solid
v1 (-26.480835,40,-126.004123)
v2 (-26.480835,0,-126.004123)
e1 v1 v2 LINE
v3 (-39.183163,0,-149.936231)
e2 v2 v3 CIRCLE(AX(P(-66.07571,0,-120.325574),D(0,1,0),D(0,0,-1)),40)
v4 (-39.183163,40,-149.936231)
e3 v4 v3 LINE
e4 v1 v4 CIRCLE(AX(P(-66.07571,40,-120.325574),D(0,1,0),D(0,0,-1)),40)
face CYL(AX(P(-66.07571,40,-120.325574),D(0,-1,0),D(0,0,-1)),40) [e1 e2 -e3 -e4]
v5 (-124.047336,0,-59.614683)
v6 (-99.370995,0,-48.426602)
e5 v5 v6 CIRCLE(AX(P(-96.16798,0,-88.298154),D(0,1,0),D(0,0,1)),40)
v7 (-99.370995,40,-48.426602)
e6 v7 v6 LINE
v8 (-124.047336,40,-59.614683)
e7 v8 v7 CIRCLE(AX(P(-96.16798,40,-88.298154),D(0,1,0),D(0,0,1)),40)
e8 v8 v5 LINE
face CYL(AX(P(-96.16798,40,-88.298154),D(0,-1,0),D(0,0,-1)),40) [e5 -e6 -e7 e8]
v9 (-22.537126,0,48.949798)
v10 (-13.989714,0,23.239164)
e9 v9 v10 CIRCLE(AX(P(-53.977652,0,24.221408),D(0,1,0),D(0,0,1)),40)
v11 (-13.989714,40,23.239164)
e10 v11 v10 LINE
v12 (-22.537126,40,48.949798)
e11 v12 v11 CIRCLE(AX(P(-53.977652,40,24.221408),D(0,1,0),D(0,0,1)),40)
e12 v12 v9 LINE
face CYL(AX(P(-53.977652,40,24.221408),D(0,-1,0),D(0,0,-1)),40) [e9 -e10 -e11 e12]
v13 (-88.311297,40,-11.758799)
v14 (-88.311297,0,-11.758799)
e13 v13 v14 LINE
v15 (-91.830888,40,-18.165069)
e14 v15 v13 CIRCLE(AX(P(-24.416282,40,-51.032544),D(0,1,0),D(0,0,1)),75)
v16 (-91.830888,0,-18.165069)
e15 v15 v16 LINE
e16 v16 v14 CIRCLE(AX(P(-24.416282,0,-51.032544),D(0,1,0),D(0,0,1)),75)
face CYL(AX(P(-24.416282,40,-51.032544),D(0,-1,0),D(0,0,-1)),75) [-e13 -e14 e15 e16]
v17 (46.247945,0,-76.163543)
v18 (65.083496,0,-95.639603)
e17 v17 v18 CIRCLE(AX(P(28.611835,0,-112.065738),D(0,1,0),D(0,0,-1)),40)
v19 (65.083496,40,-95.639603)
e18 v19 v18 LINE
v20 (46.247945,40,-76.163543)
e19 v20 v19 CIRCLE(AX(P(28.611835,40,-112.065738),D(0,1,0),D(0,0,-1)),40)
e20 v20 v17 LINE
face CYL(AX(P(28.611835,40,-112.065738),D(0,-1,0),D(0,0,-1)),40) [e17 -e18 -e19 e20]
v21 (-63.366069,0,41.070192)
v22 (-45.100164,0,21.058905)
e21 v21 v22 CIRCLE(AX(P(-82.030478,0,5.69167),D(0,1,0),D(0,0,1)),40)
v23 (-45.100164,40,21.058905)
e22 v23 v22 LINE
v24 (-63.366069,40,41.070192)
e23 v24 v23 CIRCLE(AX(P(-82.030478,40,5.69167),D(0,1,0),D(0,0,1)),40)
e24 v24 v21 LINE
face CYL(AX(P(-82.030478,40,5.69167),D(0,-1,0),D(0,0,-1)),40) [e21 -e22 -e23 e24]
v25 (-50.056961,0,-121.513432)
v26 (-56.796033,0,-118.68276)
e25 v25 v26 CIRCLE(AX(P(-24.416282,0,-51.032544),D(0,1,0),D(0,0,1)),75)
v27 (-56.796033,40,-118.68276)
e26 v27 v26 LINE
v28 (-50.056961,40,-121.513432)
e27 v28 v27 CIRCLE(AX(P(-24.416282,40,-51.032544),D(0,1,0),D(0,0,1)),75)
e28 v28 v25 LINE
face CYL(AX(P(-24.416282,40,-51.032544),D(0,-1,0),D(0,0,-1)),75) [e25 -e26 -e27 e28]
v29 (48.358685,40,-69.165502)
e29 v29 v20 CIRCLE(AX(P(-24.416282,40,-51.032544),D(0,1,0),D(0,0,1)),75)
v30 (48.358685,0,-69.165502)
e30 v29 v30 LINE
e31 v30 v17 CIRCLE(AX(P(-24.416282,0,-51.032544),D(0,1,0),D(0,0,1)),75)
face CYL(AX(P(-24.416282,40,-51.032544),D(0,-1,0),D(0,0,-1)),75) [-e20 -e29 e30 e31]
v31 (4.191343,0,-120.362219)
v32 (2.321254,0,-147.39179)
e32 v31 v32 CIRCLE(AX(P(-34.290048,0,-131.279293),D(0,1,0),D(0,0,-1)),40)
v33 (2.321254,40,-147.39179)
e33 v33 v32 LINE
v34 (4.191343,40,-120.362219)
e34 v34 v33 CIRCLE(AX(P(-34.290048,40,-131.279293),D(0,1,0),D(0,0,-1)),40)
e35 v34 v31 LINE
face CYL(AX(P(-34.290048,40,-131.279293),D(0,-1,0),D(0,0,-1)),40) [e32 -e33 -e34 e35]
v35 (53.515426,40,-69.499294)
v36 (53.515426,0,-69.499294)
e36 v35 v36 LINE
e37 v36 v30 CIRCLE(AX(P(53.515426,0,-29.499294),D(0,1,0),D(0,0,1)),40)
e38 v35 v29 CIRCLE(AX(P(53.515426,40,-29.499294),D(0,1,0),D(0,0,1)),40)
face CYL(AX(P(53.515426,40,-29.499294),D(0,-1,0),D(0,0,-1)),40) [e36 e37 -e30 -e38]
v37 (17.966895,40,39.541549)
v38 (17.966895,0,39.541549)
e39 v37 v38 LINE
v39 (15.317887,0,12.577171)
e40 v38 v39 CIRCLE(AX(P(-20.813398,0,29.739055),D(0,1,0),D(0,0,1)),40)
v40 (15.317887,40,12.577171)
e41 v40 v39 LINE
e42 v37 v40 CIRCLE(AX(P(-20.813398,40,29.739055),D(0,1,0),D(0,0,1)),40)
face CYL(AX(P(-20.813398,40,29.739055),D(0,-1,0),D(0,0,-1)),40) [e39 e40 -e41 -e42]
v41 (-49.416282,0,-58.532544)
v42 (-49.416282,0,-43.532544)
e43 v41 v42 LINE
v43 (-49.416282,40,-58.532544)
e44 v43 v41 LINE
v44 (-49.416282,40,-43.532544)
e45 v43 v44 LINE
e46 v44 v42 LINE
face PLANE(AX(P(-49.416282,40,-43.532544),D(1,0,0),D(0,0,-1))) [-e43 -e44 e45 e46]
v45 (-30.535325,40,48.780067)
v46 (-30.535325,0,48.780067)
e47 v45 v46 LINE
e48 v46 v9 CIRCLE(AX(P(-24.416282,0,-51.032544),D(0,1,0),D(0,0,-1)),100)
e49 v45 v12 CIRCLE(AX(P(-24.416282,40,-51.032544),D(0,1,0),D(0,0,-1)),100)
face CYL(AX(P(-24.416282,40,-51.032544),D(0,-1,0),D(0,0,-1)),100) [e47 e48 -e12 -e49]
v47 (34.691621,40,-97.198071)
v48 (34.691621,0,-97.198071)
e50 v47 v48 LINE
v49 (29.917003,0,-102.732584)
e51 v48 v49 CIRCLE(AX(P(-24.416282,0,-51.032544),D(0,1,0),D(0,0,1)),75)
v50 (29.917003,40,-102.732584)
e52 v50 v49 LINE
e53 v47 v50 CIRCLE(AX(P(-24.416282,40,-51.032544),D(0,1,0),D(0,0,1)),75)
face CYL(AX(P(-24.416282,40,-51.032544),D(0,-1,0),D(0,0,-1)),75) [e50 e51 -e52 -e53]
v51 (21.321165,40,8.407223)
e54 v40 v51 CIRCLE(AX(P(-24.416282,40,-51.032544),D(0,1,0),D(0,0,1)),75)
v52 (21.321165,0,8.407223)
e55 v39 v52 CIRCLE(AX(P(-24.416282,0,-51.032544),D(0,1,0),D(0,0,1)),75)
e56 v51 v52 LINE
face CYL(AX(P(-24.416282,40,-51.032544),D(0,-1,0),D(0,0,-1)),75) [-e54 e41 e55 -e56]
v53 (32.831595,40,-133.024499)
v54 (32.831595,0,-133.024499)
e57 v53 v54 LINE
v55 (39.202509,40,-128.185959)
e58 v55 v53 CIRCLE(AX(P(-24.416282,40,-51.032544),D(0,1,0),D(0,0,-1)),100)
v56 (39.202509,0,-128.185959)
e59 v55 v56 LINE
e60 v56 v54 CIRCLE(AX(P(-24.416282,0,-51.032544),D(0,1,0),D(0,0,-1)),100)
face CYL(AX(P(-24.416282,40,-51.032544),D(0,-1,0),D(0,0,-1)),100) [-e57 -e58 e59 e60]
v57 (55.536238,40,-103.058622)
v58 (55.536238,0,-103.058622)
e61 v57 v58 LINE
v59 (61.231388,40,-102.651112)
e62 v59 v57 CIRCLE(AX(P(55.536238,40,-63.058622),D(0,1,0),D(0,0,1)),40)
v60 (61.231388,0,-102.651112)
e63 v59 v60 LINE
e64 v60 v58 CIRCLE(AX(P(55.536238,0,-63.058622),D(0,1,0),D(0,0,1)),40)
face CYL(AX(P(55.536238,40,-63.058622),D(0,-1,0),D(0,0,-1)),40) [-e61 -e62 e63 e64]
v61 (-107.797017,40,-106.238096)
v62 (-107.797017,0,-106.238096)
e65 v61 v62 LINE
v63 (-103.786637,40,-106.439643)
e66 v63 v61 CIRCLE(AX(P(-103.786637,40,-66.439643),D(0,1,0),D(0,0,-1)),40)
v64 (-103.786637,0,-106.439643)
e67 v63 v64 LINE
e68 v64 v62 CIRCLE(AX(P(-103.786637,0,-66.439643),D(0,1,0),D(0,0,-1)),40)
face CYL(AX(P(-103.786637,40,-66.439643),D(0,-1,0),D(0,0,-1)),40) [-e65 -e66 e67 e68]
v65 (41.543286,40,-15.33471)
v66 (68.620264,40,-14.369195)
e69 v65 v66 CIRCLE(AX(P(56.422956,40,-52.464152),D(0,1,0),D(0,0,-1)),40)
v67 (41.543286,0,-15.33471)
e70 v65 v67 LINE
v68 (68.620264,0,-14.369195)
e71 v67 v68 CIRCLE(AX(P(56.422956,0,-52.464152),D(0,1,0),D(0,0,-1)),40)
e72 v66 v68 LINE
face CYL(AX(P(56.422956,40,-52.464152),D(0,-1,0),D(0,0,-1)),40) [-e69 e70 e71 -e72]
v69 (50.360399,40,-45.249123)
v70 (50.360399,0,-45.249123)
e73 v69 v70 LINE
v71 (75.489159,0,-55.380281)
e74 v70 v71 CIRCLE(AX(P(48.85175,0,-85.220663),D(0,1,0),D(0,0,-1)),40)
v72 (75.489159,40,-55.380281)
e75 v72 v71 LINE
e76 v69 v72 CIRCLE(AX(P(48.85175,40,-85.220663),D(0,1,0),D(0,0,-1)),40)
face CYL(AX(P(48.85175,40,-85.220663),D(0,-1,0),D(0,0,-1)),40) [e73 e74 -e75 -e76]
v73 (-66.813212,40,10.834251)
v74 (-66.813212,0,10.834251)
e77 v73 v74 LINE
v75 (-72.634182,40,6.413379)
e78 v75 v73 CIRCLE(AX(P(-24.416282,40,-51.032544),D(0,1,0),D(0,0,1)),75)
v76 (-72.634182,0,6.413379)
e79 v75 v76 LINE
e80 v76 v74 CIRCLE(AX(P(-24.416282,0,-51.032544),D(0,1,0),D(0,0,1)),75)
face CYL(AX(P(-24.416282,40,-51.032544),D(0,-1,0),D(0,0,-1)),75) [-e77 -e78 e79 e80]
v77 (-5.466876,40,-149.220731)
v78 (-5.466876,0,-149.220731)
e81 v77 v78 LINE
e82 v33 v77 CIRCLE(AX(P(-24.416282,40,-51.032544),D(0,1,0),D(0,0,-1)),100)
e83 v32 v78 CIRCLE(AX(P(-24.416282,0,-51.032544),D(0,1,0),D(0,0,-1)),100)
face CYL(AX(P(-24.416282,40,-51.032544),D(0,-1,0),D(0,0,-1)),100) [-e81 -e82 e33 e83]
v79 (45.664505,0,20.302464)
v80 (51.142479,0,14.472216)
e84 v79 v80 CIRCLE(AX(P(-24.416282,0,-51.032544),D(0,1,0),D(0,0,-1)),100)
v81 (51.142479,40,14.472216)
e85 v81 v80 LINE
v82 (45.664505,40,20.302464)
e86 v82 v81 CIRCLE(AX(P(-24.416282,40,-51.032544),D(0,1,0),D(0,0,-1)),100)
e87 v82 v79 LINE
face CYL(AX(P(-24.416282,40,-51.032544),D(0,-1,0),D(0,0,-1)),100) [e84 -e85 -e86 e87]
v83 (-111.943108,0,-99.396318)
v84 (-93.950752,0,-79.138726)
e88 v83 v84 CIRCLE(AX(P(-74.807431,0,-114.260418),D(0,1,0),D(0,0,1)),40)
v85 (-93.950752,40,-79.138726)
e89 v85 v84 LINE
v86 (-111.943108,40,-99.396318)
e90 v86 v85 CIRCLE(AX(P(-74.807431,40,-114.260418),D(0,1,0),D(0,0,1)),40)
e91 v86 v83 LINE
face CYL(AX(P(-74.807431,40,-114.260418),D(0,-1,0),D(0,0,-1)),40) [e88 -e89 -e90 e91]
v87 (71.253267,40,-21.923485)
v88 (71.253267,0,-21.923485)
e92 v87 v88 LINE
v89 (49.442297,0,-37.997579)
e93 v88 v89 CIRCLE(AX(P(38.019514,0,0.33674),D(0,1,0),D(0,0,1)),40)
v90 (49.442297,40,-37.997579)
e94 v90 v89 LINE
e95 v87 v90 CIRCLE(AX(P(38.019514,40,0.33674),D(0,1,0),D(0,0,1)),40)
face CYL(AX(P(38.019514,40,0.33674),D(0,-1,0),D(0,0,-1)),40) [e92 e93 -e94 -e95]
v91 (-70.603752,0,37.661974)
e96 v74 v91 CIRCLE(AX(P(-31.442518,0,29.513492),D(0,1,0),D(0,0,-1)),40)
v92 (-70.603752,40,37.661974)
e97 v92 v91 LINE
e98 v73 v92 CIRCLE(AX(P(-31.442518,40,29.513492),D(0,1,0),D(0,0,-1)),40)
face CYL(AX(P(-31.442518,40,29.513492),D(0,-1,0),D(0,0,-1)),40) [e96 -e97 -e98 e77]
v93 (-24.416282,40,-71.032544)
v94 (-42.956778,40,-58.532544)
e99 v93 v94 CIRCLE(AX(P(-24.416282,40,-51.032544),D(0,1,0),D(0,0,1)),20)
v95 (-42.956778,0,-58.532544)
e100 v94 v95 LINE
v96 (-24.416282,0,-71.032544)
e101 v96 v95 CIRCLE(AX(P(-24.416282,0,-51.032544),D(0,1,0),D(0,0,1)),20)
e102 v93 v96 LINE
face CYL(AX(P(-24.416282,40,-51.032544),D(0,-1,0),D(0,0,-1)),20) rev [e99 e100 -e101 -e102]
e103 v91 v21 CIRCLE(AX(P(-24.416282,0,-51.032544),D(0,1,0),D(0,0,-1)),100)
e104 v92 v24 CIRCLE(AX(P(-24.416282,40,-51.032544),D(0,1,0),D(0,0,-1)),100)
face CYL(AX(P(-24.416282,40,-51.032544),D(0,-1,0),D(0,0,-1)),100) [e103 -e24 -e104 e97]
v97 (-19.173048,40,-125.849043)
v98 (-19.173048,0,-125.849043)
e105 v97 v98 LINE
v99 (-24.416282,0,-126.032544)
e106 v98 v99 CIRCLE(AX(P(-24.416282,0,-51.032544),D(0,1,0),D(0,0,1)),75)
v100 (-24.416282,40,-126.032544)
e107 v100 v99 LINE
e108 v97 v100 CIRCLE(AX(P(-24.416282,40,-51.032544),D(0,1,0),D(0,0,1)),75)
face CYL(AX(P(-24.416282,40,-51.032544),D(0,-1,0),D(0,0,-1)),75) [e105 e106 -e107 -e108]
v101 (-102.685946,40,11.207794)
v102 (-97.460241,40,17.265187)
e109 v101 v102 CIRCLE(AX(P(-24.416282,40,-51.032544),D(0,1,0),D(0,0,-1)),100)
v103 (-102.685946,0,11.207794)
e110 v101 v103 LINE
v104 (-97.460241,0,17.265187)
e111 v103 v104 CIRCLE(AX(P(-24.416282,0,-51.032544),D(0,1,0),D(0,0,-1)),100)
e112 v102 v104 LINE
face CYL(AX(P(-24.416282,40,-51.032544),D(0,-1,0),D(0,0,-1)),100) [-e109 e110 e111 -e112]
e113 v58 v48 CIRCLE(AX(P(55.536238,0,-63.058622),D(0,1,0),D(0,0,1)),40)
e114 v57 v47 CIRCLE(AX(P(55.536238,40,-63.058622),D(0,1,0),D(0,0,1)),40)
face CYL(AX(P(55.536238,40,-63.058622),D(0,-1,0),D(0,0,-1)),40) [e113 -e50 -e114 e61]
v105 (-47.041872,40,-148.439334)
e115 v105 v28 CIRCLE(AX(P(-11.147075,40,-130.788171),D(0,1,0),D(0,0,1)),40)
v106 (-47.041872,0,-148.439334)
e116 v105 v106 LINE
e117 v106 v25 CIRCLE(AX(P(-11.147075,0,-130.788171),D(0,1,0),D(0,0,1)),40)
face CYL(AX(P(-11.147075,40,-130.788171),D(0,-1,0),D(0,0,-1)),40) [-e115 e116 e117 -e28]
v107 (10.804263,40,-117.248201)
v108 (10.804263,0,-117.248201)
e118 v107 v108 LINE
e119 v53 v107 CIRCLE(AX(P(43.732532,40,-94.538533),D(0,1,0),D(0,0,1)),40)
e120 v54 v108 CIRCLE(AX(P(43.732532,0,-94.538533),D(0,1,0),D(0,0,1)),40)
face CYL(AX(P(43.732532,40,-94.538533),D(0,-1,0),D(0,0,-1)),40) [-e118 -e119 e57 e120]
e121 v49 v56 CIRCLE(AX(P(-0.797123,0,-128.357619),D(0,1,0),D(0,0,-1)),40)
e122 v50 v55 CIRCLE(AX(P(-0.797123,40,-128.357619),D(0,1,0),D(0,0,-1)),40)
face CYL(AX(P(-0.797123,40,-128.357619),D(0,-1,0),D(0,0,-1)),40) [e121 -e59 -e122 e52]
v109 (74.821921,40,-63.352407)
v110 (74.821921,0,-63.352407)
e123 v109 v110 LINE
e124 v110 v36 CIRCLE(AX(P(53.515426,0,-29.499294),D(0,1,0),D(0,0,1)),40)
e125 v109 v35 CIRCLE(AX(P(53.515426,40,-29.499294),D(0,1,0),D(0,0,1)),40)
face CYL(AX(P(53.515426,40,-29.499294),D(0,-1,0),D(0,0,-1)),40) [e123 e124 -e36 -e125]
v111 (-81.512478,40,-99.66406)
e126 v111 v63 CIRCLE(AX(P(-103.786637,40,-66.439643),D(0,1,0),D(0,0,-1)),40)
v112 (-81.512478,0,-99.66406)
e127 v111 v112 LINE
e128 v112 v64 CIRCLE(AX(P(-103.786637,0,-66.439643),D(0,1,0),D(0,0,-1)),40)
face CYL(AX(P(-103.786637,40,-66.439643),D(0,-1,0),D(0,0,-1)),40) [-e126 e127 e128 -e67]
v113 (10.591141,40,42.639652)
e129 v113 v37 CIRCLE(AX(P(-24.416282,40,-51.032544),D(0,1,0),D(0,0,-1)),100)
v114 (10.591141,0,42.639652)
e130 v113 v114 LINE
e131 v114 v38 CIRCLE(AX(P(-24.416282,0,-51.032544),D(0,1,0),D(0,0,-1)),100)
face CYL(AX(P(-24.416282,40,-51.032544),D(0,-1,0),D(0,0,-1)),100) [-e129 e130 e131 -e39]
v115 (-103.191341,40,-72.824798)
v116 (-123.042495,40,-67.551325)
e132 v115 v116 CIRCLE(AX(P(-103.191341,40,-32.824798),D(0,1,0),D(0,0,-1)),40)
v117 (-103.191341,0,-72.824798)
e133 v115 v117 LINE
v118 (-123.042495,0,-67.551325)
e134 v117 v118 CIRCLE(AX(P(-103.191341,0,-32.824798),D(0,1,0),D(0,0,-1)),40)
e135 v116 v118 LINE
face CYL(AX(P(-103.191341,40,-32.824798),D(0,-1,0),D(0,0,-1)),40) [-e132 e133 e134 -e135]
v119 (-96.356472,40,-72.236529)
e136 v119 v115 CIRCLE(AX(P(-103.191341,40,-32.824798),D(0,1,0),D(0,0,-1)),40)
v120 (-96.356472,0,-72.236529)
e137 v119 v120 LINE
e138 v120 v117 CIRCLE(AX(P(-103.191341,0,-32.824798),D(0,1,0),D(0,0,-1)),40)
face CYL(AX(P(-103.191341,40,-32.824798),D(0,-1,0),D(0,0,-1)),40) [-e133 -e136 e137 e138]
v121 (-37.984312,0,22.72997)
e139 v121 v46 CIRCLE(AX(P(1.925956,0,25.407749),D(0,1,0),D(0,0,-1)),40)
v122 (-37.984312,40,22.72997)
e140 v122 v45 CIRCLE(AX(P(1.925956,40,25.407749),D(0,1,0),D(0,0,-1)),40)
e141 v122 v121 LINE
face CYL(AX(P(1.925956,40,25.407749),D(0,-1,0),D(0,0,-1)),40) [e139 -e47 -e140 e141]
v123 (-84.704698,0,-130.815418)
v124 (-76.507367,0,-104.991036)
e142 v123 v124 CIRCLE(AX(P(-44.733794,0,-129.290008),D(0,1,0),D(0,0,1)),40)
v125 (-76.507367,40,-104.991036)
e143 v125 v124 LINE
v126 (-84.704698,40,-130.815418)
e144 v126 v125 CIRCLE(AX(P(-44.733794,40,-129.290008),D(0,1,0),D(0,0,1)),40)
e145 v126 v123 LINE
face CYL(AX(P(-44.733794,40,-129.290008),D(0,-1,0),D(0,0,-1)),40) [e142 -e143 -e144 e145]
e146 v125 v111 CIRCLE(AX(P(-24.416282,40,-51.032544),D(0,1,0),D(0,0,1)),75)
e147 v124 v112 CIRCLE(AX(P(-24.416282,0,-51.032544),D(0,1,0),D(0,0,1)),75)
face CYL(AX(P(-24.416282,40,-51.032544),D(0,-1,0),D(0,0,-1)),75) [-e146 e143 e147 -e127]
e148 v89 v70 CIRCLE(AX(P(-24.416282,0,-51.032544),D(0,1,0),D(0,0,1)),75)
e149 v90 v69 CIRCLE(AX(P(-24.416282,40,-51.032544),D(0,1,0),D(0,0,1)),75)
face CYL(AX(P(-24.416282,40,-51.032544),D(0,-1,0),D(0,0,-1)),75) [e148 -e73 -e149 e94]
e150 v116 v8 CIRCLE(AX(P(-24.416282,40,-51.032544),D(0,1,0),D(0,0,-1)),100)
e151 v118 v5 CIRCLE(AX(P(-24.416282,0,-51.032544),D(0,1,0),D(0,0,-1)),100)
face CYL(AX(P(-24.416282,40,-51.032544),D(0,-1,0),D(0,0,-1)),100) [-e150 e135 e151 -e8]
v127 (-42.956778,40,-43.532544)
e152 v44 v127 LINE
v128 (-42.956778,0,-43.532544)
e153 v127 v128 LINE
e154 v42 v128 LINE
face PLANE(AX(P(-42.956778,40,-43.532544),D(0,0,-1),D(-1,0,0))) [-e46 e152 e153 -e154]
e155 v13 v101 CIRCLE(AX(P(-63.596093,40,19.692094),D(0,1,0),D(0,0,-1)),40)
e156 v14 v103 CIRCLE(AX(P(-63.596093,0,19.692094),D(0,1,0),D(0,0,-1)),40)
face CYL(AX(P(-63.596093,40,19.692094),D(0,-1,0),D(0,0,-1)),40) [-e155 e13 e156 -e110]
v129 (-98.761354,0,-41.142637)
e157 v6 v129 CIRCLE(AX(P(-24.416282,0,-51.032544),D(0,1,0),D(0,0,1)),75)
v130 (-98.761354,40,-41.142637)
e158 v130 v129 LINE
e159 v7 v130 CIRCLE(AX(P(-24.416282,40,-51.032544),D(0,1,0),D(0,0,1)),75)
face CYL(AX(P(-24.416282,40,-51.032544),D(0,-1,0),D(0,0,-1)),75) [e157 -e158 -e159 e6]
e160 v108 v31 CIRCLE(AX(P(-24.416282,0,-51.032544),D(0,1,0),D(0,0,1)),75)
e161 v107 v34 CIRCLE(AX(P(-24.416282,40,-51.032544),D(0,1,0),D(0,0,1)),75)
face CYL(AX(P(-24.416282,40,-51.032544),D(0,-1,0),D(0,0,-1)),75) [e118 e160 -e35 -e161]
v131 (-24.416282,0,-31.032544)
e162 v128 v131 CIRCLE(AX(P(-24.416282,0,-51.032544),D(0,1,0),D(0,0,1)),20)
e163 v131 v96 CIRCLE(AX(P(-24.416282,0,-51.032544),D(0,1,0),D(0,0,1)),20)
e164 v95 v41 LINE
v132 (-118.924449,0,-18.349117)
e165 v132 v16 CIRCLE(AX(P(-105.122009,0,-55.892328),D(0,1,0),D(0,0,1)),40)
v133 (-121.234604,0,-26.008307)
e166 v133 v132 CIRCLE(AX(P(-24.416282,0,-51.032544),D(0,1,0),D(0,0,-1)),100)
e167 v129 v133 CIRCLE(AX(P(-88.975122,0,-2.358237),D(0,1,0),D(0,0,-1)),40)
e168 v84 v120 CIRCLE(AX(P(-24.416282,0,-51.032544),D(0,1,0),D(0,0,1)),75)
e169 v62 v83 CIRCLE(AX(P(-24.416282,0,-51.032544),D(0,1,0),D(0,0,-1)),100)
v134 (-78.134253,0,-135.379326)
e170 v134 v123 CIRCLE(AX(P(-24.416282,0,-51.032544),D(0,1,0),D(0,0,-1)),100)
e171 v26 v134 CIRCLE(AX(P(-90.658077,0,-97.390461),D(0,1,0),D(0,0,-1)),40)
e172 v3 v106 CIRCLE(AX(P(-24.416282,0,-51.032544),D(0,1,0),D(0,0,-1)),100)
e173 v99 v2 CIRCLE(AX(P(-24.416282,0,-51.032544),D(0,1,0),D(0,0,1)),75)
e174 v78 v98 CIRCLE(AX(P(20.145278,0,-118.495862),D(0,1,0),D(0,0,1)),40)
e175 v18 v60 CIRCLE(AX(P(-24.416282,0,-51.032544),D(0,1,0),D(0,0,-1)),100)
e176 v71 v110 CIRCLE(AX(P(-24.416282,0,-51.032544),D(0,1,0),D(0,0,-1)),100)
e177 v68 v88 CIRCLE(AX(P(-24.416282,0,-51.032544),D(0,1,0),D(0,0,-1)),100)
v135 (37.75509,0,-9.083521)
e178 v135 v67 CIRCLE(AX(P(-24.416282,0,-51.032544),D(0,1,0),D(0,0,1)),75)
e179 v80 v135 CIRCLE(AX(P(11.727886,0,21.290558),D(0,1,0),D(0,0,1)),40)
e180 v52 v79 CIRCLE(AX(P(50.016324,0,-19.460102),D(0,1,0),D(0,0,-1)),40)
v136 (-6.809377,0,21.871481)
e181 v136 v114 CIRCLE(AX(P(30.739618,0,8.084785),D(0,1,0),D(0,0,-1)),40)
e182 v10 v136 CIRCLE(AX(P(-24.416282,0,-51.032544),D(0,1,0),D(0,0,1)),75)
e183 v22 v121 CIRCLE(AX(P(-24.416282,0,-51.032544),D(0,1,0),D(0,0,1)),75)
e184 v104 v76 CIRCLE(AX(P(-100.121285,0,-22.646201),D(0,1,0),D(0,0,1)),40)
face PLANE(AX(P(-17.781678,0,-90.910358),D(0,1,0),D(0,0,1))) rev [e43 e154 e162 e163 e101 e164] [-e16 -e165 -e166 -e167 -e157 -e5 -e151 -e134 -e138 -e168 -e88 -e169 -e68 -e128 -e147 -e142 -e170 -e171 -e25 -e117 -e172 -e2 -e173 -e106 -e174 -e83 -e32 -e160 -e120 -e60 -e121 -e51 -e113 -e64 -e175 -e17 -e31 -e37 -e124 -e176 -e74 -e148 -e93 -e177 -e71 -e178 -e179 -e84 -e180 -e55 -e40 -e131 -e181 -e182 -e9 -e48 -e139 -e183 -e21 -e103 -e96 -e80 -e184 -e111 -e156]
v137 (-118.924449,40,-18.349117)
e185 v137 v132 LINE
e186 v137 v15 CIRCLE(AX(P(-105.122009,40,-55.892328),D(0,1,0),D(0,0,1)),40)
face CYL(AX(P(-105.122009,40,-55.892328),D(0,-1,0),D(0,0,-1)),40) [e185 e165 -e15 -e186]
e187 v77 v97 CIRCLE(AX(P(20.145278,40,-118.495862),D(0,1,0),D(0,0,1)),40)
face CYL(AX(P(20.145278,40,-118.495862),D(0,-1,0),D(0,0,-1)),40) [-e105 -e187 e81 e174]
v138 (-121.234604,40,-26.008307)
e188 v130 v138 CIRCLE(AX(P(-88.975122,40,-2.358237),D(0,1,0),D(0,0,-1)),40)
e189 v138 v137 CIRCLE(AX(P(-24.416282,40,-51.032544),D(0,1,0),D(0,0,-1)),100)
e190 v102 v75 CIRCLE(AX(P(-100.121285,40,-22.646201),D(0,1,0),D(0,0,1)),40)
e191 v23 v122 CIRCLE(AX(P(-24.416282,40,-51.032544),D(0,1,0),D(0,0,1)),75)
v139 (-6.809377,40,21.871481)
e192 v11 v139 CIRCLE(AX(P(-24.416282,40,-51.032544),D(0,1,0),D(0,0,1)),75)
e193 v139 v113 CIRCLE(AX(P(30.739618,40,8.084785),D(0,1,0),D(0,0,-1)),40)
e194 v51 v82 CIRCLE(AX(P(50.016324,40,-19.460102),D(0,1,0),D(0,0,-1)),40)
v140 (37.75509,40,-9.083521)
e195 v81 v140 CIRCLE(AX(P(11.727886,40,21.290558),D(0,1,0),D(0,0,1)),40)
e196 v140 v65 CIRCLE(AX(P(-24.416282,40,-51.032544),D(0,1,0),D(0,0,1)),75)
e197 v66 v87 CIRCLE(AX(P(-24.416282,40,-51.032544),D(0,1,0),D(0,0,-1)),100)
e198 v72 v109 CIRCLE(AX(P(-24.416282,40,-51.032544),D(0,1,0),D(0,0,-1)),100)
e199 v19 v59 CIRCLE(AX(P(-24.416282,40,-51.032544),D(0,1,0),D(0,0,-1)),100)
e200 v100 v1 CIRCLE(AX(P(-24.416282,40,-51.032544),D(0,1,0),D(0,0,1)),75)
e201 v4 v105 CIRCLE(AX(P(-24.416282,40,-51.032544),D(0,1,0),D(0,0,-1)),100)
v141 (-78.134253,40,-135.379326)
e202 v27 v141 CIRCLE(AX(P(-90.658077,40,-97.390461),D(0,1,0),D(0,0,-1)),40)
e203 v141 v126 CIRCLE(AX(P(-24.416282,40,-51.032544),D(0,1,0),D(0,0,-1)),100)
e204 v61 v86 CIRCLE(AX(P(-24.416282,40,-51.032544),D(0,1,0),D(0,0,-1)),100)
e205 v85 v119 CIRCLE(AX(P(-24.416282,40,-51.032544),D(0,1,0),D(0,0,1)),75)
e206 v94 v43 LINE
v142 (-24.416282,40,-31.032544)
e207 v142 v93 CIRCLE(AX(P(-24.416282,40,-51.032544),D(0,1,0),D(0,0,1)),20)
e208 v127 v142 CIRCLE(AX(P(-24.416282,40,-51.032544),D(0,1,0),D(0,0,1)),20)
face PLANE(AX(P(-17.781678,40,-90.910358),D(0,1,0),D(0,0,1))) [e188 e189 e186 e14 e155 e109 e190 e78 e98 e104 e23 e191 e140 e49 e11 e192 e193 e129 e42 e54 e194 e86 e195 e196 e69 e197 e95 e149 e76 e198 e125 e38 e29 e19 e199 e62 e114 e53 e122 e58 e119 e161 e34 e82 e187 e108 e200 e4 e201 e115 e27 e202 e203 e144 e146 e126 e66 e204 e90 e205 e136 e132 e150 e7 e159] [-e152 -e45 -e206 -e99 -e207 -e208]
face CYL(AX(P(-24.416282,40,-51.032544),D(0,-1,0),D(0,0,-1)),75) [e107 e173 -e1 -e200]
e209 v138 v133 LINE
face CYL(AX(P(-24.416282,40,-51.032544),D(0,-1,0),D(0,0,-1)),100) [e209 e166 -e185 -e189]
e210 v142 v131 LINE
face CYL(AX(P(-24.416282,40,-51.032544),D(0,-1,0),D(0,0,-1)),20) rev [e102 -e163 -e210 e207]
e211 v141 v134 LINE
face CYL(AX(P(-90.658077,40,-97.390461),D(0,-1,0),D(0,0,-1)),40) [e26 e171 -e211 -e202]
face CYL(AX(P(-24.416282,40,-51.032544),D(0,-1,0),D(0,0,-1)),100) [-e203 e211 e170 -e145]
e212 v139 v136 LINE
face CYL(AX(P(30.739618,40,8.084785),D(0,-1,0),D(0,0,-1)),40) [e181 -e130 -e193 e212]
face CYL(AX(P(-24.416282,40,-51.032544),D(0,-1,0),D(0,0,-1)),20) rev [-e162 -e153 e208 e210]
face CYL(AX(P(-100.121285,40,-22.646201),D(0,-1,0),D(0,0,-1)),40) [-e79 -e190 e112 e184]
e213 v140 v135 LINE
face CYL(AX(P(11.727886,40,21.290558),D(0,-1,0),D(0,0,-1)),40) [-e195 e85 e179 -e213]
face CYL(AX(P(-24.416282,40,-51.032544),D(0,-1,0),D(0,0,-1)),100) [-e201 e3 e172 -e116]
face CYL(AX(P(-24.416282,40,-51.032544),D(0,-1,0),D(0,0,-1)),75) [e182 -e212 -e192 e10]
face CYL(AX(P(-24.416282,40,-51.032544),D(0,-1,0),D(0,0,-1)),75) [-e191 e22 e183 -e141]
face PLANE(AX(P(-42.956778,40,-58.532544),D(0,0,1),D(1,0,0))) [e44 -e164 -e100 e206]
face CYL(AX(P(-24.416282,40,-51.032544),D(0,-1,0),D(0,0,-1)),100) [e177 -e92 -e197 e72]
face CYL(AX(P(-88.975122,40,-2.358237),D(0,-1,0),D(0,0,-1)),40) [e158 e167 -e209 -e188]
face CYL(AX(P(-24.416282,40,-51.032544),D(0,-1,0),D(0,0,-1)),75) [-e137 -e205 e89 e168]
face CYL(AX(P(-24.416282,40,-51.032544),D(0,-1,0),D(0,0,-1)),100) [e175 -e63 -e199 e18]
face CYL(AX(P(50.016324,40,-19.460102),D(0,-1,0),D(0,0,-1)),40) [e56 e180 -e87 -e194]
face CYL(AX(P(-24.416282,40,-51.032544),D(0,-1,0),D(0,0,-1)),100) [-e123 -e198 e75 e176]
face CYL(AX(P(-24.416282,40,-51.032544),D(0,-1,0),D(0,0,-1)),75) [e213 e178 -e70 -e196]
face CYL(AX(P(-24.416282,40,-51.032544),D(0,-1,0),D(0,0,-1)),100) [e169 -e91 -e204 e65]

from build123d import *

# Parameters (mm, degrees)
BOSS_EXTRUDE1_DEPTH = 40


with BuildPart() as part:
    # Sketch1 → Boss-Extrude1 (new body)
    with BuildSketch(Plane(origin=(0, 0, 0), x_dir=(1, 0, 0), z_dir=(0, 1, 0))):
        with BuildLine():
            ThreePointArc((-47.041872024, 148.439333774), (-43.127492719, 149.266400751), (-39.183163492, 149.936230637))
            ThreePointArc((-39.183163492, 149.936230637), (-30.743985568, 139.078421622), (-26.480835029, 126.00412286))
            ThreePointArc((-26.480835029, 126.00412286), (-22.825050962, 126.015662102), (-19.173047629, 125.849042918))
            ThreePointArc((-19.173047629, 125.849042918), (-14.359080523, 138.730714445), (-5.466876345, 149.220730913))
            ThreePointArc((-5.466876345, 149.220730913), (-1.554514466, 148.384172695), (2.321253942, 147.391789516))
            ThreePointArc((2.321253942, 147.391789516), (5.614557811, 134.040164511), (4.191343232, 120.362218726))
            ThreePointArc((4.191343232, 120.362218726), (7.535761593, 118.885819009), (10.804262521, 117.248201234))
            ThreePointArc((10.804262521, 117.248201234), (20.441488139, 127.058176924), (32.831594958, 133.024498542))
            ThreePointArc((32.831594958, 133.024498542), (36.0654565, 130.668963645), (39.202508521, 128.185959468))
            ThreePointArc((39.202508521, 128.185959468), (36.780496177, 114.649135732), (29.91700321, 102.732584011))
            ThreePointArc((29.91700321, 102.732584011), (32.371775547, 100.023528258), (34.691620567, 97.198070883))
            ThreePointArc((34.691620567, 97.198070883), (47.485740835, 102.240116818), (61.231388266, 102.651112376))
            ThreePointArc((61.231388266, 102.651112376), (63.227585431, 99.183894183), (65.083496272, 95.639602987))
            ThreePointArc((65.083496272, 95.639602987), (57.364955653, 84.258220323), (46.247944585, 76.163542716))
            ThreePointArc((46.247944585, 76.163542716), (47.388618461, 72.690251279), (48.358685293, 69.165501552))
            ThreePointArc((48.358685293, 69.165501552), (62.097480586, 68.567802184), (74.821921313, 63.352406817))
            ThreePointArc((74.821921313, 63.352406817), (75.235293477, 59.373018851), (75.489159292, 55.380280784))
            ThreePointArc((75.489159292, 55.380280784), (63.808696192, 48.12228365), (50.360399232, 45.249123454))
            ThreePointArc((50.360399232, 45.249123454), (49.98974177, 41.612159976), (49.442297047, 37.997579146))
            ThreePointArc((49.442297047, 37.997579146), (61.750204846, 31.863482126), (71.253267468, 21.923485072))
            ThreePointArc((71.253267468, 21.923485072), (70.012338829, 18.119999666), (68.620263913, 14.369195412))
            ThreePointArc((68.620263913, 14.369195412), (54.997536515, 12.48955745), (41.543286381, 15.334710164))
            ThreePointArc((41.543286381, 15.334710164), (39.725387624, 12.162938671), (37.755089511, 9.083520601))
            ThreePointArc((37.755089511, 9.083520601), (46.503960743, -1.526332969), (51.142479402, -14.472215917))
            ThreePointArc((51.142479402, -14.472215917), (48.461817794, -17.442141584), (45.664504547, -20.302463895))
            ThreePointArc((45.664504547, -20.302463895), (32.455006176, -16.478736206), (21.321164945, -8.407223332))
            ThreePointArc((21.321164945, -8.407223332), (18.370356103, -10.565374735), (15.317887044, -12.577170684))
            ThreePointArc((15.317887044, -12.577170684), (18.994962393, -25.828240736), (17.966895072, -39.541548806))
            ThreePointArc((17.966895072, -39.541548806), (14.31001124, -41.164387605), (10.591140535, -42.639652259))
            ThreePointArc((10.591140535, -42.639652259), (0.078913465, -33.773716174), (-6.809376568, -21.871481045))
            ThreePointArc((-6.809376568, -21.871481045), (-10.382873838, -22.642848373), (-13.989714213, -23.239164406))
            ThreePointArc((-13.989714213, -23.239164406), (-16.02023448, -36.840220544), (-22.537125601, -48.94979819))
            ThreePointArc((-22.537125601, -48.94979819), (-26.53792322, -48.944946549), (-30.535324854, -48.780066887))
            ThreePointArc((-30.535324854, -48.780066887), (-36.532621062, -36.404923299), (-37.984311971, -22.729970496))
            ThreePointArc((-37.984311971, -22.729970496), (-41.562607528, -21.981177331), (-45.10016375, -21.058904988))
            ThreePointArc((-45.10016375, -21.058904988), (-52.487184233, -32.658201045), (-63.366069475, -41.07019228))
            ThreePointArc((-63.366069475, -41.07019228), (-67.019006626, -39.438489092), (-70.603752131, -37.661974304))
            ThreePointArc((-70.603752131, -37.661974304), (-71.049130479, -23.917397964), (-66.813211718, -10.834251061))
            ThreePointArc((-66.813211718, -10.834251061), (-69.777585752, -8.694770544), (-72.634182213, -6.413379092))
            ThreePointArc((-72.634182213, -6.413379092), (-84.100419961, -14.005291403), (-97.460241234, -17.265186521))
            ThreePointArc((-97.460241234, -17.265186521), (-100.133691899, -14.288768092), (-102.68594621, -11.207793723))
            ThreePointArc((-102.68594621, -11.207793723), (-97.502396736, 1.529653253), (-88.311297141, 11.758799301))
            ThreePointArc((-88.311297141, 11.758799301), (-90.149182451, 14.919031553), (-91.830887671, 18.165068806))
            ThreePointArc((-91.830887671, 18.165068806), (-105.39372601, 15.89325085), (-118.924448847, 18.349117329))
            ThreePointArc((-118.924448847, 18.349117329), (-120.156149117, 22.155601214), (-121.234604278, 26.008306704))
            ThreePointArc((-121.234604278, 26.008306704), (-111.318409777, 35.53620402), (-98.761353966, 41.142636931))
            ThreePointArc((-98.761353966, 41.142636931), (-99.154963485, 44.777188051), (-99.370995354, 48.426601775))
            ThreePointArc((-99.370995354, 48.426601775), (-112.685296321, 51.867696137), (-124.047335819, 59.614682589))
            ThreePointArc((-124.047335819, 59.614682589), (-123.624313529, 63.593056285), (-123.042494845, 67.551325117))
            ThreePointArc((-123.042494845, 67.551325117), (-110.108255432, 72.222212767), (-96.356472432, 72.236529359))
            ThreePointArc((-96.356472432, 72.236529359), (-95.237747499, 75.71695244), (-93.950752144, 79.138725848))
            ThreePointArc((-93.950752144, 79.138725848), (-104.714352145, 87.697736052), (-111.943108455, 99.396318139))
            ThreePointArc((-111.943108455, 99.396318139), (-109.938508001, 102.858684692), (-107.797017208, 106.238096225))
            ThreePointArc((-107.797017208, 106.238096225), (-94.081180381, 105.244335301), (-81.512478404, 99.664060105))
            ThreePointArc((-81.512478404, 99.664060105), (-79.074856723, 102.388558378), (-76.507367333, 104.991035762))
            ThreePointArc((-76.507367333, 104.991035762), (-82.859142143, 117.188031187), (-84.704697628, 130.815417788))
            ThreePointArc((-84.704697628, 130.815417788), (-81.46513264, 133.163102566), (-78.134252951, 135.379325845))
            ThreePointArc((-78.134252951, 135.379325845), (-66.008411502, 128.892746639), (-56.796033303, 118.682759932))
            ThreePointArc((-56.796033303, 118.682759932), (-53.461001807, 120.180242893), (-50.056960623, 121.513432271))
            ThreePointArc((-50.056960623, 121.513432271), (-50.898630674, 135.239441602), (-47.041872024, 148.439333774))
        make_face()
        with BuildLine():
            Line((-42.956778148, 58.532544108), (-49.41628193, 58.532544108))
            Line((-49.41628193, 58.532544108), (-49.41628193, 43.532544108))
            Line((-49.41628193, 43.532544108), (-42.956778148, 43.532544108))
            ThreePointArc((-42.956778148, 43.532544108), (-4.41628193, 51.032544108), (-42.956778148, 58.532544108))
        make_face(mode=Mode.SUBTRACT)
    extrude(amount=BOSS_EXTRUDE1_DEPTH)


solid = part.part
